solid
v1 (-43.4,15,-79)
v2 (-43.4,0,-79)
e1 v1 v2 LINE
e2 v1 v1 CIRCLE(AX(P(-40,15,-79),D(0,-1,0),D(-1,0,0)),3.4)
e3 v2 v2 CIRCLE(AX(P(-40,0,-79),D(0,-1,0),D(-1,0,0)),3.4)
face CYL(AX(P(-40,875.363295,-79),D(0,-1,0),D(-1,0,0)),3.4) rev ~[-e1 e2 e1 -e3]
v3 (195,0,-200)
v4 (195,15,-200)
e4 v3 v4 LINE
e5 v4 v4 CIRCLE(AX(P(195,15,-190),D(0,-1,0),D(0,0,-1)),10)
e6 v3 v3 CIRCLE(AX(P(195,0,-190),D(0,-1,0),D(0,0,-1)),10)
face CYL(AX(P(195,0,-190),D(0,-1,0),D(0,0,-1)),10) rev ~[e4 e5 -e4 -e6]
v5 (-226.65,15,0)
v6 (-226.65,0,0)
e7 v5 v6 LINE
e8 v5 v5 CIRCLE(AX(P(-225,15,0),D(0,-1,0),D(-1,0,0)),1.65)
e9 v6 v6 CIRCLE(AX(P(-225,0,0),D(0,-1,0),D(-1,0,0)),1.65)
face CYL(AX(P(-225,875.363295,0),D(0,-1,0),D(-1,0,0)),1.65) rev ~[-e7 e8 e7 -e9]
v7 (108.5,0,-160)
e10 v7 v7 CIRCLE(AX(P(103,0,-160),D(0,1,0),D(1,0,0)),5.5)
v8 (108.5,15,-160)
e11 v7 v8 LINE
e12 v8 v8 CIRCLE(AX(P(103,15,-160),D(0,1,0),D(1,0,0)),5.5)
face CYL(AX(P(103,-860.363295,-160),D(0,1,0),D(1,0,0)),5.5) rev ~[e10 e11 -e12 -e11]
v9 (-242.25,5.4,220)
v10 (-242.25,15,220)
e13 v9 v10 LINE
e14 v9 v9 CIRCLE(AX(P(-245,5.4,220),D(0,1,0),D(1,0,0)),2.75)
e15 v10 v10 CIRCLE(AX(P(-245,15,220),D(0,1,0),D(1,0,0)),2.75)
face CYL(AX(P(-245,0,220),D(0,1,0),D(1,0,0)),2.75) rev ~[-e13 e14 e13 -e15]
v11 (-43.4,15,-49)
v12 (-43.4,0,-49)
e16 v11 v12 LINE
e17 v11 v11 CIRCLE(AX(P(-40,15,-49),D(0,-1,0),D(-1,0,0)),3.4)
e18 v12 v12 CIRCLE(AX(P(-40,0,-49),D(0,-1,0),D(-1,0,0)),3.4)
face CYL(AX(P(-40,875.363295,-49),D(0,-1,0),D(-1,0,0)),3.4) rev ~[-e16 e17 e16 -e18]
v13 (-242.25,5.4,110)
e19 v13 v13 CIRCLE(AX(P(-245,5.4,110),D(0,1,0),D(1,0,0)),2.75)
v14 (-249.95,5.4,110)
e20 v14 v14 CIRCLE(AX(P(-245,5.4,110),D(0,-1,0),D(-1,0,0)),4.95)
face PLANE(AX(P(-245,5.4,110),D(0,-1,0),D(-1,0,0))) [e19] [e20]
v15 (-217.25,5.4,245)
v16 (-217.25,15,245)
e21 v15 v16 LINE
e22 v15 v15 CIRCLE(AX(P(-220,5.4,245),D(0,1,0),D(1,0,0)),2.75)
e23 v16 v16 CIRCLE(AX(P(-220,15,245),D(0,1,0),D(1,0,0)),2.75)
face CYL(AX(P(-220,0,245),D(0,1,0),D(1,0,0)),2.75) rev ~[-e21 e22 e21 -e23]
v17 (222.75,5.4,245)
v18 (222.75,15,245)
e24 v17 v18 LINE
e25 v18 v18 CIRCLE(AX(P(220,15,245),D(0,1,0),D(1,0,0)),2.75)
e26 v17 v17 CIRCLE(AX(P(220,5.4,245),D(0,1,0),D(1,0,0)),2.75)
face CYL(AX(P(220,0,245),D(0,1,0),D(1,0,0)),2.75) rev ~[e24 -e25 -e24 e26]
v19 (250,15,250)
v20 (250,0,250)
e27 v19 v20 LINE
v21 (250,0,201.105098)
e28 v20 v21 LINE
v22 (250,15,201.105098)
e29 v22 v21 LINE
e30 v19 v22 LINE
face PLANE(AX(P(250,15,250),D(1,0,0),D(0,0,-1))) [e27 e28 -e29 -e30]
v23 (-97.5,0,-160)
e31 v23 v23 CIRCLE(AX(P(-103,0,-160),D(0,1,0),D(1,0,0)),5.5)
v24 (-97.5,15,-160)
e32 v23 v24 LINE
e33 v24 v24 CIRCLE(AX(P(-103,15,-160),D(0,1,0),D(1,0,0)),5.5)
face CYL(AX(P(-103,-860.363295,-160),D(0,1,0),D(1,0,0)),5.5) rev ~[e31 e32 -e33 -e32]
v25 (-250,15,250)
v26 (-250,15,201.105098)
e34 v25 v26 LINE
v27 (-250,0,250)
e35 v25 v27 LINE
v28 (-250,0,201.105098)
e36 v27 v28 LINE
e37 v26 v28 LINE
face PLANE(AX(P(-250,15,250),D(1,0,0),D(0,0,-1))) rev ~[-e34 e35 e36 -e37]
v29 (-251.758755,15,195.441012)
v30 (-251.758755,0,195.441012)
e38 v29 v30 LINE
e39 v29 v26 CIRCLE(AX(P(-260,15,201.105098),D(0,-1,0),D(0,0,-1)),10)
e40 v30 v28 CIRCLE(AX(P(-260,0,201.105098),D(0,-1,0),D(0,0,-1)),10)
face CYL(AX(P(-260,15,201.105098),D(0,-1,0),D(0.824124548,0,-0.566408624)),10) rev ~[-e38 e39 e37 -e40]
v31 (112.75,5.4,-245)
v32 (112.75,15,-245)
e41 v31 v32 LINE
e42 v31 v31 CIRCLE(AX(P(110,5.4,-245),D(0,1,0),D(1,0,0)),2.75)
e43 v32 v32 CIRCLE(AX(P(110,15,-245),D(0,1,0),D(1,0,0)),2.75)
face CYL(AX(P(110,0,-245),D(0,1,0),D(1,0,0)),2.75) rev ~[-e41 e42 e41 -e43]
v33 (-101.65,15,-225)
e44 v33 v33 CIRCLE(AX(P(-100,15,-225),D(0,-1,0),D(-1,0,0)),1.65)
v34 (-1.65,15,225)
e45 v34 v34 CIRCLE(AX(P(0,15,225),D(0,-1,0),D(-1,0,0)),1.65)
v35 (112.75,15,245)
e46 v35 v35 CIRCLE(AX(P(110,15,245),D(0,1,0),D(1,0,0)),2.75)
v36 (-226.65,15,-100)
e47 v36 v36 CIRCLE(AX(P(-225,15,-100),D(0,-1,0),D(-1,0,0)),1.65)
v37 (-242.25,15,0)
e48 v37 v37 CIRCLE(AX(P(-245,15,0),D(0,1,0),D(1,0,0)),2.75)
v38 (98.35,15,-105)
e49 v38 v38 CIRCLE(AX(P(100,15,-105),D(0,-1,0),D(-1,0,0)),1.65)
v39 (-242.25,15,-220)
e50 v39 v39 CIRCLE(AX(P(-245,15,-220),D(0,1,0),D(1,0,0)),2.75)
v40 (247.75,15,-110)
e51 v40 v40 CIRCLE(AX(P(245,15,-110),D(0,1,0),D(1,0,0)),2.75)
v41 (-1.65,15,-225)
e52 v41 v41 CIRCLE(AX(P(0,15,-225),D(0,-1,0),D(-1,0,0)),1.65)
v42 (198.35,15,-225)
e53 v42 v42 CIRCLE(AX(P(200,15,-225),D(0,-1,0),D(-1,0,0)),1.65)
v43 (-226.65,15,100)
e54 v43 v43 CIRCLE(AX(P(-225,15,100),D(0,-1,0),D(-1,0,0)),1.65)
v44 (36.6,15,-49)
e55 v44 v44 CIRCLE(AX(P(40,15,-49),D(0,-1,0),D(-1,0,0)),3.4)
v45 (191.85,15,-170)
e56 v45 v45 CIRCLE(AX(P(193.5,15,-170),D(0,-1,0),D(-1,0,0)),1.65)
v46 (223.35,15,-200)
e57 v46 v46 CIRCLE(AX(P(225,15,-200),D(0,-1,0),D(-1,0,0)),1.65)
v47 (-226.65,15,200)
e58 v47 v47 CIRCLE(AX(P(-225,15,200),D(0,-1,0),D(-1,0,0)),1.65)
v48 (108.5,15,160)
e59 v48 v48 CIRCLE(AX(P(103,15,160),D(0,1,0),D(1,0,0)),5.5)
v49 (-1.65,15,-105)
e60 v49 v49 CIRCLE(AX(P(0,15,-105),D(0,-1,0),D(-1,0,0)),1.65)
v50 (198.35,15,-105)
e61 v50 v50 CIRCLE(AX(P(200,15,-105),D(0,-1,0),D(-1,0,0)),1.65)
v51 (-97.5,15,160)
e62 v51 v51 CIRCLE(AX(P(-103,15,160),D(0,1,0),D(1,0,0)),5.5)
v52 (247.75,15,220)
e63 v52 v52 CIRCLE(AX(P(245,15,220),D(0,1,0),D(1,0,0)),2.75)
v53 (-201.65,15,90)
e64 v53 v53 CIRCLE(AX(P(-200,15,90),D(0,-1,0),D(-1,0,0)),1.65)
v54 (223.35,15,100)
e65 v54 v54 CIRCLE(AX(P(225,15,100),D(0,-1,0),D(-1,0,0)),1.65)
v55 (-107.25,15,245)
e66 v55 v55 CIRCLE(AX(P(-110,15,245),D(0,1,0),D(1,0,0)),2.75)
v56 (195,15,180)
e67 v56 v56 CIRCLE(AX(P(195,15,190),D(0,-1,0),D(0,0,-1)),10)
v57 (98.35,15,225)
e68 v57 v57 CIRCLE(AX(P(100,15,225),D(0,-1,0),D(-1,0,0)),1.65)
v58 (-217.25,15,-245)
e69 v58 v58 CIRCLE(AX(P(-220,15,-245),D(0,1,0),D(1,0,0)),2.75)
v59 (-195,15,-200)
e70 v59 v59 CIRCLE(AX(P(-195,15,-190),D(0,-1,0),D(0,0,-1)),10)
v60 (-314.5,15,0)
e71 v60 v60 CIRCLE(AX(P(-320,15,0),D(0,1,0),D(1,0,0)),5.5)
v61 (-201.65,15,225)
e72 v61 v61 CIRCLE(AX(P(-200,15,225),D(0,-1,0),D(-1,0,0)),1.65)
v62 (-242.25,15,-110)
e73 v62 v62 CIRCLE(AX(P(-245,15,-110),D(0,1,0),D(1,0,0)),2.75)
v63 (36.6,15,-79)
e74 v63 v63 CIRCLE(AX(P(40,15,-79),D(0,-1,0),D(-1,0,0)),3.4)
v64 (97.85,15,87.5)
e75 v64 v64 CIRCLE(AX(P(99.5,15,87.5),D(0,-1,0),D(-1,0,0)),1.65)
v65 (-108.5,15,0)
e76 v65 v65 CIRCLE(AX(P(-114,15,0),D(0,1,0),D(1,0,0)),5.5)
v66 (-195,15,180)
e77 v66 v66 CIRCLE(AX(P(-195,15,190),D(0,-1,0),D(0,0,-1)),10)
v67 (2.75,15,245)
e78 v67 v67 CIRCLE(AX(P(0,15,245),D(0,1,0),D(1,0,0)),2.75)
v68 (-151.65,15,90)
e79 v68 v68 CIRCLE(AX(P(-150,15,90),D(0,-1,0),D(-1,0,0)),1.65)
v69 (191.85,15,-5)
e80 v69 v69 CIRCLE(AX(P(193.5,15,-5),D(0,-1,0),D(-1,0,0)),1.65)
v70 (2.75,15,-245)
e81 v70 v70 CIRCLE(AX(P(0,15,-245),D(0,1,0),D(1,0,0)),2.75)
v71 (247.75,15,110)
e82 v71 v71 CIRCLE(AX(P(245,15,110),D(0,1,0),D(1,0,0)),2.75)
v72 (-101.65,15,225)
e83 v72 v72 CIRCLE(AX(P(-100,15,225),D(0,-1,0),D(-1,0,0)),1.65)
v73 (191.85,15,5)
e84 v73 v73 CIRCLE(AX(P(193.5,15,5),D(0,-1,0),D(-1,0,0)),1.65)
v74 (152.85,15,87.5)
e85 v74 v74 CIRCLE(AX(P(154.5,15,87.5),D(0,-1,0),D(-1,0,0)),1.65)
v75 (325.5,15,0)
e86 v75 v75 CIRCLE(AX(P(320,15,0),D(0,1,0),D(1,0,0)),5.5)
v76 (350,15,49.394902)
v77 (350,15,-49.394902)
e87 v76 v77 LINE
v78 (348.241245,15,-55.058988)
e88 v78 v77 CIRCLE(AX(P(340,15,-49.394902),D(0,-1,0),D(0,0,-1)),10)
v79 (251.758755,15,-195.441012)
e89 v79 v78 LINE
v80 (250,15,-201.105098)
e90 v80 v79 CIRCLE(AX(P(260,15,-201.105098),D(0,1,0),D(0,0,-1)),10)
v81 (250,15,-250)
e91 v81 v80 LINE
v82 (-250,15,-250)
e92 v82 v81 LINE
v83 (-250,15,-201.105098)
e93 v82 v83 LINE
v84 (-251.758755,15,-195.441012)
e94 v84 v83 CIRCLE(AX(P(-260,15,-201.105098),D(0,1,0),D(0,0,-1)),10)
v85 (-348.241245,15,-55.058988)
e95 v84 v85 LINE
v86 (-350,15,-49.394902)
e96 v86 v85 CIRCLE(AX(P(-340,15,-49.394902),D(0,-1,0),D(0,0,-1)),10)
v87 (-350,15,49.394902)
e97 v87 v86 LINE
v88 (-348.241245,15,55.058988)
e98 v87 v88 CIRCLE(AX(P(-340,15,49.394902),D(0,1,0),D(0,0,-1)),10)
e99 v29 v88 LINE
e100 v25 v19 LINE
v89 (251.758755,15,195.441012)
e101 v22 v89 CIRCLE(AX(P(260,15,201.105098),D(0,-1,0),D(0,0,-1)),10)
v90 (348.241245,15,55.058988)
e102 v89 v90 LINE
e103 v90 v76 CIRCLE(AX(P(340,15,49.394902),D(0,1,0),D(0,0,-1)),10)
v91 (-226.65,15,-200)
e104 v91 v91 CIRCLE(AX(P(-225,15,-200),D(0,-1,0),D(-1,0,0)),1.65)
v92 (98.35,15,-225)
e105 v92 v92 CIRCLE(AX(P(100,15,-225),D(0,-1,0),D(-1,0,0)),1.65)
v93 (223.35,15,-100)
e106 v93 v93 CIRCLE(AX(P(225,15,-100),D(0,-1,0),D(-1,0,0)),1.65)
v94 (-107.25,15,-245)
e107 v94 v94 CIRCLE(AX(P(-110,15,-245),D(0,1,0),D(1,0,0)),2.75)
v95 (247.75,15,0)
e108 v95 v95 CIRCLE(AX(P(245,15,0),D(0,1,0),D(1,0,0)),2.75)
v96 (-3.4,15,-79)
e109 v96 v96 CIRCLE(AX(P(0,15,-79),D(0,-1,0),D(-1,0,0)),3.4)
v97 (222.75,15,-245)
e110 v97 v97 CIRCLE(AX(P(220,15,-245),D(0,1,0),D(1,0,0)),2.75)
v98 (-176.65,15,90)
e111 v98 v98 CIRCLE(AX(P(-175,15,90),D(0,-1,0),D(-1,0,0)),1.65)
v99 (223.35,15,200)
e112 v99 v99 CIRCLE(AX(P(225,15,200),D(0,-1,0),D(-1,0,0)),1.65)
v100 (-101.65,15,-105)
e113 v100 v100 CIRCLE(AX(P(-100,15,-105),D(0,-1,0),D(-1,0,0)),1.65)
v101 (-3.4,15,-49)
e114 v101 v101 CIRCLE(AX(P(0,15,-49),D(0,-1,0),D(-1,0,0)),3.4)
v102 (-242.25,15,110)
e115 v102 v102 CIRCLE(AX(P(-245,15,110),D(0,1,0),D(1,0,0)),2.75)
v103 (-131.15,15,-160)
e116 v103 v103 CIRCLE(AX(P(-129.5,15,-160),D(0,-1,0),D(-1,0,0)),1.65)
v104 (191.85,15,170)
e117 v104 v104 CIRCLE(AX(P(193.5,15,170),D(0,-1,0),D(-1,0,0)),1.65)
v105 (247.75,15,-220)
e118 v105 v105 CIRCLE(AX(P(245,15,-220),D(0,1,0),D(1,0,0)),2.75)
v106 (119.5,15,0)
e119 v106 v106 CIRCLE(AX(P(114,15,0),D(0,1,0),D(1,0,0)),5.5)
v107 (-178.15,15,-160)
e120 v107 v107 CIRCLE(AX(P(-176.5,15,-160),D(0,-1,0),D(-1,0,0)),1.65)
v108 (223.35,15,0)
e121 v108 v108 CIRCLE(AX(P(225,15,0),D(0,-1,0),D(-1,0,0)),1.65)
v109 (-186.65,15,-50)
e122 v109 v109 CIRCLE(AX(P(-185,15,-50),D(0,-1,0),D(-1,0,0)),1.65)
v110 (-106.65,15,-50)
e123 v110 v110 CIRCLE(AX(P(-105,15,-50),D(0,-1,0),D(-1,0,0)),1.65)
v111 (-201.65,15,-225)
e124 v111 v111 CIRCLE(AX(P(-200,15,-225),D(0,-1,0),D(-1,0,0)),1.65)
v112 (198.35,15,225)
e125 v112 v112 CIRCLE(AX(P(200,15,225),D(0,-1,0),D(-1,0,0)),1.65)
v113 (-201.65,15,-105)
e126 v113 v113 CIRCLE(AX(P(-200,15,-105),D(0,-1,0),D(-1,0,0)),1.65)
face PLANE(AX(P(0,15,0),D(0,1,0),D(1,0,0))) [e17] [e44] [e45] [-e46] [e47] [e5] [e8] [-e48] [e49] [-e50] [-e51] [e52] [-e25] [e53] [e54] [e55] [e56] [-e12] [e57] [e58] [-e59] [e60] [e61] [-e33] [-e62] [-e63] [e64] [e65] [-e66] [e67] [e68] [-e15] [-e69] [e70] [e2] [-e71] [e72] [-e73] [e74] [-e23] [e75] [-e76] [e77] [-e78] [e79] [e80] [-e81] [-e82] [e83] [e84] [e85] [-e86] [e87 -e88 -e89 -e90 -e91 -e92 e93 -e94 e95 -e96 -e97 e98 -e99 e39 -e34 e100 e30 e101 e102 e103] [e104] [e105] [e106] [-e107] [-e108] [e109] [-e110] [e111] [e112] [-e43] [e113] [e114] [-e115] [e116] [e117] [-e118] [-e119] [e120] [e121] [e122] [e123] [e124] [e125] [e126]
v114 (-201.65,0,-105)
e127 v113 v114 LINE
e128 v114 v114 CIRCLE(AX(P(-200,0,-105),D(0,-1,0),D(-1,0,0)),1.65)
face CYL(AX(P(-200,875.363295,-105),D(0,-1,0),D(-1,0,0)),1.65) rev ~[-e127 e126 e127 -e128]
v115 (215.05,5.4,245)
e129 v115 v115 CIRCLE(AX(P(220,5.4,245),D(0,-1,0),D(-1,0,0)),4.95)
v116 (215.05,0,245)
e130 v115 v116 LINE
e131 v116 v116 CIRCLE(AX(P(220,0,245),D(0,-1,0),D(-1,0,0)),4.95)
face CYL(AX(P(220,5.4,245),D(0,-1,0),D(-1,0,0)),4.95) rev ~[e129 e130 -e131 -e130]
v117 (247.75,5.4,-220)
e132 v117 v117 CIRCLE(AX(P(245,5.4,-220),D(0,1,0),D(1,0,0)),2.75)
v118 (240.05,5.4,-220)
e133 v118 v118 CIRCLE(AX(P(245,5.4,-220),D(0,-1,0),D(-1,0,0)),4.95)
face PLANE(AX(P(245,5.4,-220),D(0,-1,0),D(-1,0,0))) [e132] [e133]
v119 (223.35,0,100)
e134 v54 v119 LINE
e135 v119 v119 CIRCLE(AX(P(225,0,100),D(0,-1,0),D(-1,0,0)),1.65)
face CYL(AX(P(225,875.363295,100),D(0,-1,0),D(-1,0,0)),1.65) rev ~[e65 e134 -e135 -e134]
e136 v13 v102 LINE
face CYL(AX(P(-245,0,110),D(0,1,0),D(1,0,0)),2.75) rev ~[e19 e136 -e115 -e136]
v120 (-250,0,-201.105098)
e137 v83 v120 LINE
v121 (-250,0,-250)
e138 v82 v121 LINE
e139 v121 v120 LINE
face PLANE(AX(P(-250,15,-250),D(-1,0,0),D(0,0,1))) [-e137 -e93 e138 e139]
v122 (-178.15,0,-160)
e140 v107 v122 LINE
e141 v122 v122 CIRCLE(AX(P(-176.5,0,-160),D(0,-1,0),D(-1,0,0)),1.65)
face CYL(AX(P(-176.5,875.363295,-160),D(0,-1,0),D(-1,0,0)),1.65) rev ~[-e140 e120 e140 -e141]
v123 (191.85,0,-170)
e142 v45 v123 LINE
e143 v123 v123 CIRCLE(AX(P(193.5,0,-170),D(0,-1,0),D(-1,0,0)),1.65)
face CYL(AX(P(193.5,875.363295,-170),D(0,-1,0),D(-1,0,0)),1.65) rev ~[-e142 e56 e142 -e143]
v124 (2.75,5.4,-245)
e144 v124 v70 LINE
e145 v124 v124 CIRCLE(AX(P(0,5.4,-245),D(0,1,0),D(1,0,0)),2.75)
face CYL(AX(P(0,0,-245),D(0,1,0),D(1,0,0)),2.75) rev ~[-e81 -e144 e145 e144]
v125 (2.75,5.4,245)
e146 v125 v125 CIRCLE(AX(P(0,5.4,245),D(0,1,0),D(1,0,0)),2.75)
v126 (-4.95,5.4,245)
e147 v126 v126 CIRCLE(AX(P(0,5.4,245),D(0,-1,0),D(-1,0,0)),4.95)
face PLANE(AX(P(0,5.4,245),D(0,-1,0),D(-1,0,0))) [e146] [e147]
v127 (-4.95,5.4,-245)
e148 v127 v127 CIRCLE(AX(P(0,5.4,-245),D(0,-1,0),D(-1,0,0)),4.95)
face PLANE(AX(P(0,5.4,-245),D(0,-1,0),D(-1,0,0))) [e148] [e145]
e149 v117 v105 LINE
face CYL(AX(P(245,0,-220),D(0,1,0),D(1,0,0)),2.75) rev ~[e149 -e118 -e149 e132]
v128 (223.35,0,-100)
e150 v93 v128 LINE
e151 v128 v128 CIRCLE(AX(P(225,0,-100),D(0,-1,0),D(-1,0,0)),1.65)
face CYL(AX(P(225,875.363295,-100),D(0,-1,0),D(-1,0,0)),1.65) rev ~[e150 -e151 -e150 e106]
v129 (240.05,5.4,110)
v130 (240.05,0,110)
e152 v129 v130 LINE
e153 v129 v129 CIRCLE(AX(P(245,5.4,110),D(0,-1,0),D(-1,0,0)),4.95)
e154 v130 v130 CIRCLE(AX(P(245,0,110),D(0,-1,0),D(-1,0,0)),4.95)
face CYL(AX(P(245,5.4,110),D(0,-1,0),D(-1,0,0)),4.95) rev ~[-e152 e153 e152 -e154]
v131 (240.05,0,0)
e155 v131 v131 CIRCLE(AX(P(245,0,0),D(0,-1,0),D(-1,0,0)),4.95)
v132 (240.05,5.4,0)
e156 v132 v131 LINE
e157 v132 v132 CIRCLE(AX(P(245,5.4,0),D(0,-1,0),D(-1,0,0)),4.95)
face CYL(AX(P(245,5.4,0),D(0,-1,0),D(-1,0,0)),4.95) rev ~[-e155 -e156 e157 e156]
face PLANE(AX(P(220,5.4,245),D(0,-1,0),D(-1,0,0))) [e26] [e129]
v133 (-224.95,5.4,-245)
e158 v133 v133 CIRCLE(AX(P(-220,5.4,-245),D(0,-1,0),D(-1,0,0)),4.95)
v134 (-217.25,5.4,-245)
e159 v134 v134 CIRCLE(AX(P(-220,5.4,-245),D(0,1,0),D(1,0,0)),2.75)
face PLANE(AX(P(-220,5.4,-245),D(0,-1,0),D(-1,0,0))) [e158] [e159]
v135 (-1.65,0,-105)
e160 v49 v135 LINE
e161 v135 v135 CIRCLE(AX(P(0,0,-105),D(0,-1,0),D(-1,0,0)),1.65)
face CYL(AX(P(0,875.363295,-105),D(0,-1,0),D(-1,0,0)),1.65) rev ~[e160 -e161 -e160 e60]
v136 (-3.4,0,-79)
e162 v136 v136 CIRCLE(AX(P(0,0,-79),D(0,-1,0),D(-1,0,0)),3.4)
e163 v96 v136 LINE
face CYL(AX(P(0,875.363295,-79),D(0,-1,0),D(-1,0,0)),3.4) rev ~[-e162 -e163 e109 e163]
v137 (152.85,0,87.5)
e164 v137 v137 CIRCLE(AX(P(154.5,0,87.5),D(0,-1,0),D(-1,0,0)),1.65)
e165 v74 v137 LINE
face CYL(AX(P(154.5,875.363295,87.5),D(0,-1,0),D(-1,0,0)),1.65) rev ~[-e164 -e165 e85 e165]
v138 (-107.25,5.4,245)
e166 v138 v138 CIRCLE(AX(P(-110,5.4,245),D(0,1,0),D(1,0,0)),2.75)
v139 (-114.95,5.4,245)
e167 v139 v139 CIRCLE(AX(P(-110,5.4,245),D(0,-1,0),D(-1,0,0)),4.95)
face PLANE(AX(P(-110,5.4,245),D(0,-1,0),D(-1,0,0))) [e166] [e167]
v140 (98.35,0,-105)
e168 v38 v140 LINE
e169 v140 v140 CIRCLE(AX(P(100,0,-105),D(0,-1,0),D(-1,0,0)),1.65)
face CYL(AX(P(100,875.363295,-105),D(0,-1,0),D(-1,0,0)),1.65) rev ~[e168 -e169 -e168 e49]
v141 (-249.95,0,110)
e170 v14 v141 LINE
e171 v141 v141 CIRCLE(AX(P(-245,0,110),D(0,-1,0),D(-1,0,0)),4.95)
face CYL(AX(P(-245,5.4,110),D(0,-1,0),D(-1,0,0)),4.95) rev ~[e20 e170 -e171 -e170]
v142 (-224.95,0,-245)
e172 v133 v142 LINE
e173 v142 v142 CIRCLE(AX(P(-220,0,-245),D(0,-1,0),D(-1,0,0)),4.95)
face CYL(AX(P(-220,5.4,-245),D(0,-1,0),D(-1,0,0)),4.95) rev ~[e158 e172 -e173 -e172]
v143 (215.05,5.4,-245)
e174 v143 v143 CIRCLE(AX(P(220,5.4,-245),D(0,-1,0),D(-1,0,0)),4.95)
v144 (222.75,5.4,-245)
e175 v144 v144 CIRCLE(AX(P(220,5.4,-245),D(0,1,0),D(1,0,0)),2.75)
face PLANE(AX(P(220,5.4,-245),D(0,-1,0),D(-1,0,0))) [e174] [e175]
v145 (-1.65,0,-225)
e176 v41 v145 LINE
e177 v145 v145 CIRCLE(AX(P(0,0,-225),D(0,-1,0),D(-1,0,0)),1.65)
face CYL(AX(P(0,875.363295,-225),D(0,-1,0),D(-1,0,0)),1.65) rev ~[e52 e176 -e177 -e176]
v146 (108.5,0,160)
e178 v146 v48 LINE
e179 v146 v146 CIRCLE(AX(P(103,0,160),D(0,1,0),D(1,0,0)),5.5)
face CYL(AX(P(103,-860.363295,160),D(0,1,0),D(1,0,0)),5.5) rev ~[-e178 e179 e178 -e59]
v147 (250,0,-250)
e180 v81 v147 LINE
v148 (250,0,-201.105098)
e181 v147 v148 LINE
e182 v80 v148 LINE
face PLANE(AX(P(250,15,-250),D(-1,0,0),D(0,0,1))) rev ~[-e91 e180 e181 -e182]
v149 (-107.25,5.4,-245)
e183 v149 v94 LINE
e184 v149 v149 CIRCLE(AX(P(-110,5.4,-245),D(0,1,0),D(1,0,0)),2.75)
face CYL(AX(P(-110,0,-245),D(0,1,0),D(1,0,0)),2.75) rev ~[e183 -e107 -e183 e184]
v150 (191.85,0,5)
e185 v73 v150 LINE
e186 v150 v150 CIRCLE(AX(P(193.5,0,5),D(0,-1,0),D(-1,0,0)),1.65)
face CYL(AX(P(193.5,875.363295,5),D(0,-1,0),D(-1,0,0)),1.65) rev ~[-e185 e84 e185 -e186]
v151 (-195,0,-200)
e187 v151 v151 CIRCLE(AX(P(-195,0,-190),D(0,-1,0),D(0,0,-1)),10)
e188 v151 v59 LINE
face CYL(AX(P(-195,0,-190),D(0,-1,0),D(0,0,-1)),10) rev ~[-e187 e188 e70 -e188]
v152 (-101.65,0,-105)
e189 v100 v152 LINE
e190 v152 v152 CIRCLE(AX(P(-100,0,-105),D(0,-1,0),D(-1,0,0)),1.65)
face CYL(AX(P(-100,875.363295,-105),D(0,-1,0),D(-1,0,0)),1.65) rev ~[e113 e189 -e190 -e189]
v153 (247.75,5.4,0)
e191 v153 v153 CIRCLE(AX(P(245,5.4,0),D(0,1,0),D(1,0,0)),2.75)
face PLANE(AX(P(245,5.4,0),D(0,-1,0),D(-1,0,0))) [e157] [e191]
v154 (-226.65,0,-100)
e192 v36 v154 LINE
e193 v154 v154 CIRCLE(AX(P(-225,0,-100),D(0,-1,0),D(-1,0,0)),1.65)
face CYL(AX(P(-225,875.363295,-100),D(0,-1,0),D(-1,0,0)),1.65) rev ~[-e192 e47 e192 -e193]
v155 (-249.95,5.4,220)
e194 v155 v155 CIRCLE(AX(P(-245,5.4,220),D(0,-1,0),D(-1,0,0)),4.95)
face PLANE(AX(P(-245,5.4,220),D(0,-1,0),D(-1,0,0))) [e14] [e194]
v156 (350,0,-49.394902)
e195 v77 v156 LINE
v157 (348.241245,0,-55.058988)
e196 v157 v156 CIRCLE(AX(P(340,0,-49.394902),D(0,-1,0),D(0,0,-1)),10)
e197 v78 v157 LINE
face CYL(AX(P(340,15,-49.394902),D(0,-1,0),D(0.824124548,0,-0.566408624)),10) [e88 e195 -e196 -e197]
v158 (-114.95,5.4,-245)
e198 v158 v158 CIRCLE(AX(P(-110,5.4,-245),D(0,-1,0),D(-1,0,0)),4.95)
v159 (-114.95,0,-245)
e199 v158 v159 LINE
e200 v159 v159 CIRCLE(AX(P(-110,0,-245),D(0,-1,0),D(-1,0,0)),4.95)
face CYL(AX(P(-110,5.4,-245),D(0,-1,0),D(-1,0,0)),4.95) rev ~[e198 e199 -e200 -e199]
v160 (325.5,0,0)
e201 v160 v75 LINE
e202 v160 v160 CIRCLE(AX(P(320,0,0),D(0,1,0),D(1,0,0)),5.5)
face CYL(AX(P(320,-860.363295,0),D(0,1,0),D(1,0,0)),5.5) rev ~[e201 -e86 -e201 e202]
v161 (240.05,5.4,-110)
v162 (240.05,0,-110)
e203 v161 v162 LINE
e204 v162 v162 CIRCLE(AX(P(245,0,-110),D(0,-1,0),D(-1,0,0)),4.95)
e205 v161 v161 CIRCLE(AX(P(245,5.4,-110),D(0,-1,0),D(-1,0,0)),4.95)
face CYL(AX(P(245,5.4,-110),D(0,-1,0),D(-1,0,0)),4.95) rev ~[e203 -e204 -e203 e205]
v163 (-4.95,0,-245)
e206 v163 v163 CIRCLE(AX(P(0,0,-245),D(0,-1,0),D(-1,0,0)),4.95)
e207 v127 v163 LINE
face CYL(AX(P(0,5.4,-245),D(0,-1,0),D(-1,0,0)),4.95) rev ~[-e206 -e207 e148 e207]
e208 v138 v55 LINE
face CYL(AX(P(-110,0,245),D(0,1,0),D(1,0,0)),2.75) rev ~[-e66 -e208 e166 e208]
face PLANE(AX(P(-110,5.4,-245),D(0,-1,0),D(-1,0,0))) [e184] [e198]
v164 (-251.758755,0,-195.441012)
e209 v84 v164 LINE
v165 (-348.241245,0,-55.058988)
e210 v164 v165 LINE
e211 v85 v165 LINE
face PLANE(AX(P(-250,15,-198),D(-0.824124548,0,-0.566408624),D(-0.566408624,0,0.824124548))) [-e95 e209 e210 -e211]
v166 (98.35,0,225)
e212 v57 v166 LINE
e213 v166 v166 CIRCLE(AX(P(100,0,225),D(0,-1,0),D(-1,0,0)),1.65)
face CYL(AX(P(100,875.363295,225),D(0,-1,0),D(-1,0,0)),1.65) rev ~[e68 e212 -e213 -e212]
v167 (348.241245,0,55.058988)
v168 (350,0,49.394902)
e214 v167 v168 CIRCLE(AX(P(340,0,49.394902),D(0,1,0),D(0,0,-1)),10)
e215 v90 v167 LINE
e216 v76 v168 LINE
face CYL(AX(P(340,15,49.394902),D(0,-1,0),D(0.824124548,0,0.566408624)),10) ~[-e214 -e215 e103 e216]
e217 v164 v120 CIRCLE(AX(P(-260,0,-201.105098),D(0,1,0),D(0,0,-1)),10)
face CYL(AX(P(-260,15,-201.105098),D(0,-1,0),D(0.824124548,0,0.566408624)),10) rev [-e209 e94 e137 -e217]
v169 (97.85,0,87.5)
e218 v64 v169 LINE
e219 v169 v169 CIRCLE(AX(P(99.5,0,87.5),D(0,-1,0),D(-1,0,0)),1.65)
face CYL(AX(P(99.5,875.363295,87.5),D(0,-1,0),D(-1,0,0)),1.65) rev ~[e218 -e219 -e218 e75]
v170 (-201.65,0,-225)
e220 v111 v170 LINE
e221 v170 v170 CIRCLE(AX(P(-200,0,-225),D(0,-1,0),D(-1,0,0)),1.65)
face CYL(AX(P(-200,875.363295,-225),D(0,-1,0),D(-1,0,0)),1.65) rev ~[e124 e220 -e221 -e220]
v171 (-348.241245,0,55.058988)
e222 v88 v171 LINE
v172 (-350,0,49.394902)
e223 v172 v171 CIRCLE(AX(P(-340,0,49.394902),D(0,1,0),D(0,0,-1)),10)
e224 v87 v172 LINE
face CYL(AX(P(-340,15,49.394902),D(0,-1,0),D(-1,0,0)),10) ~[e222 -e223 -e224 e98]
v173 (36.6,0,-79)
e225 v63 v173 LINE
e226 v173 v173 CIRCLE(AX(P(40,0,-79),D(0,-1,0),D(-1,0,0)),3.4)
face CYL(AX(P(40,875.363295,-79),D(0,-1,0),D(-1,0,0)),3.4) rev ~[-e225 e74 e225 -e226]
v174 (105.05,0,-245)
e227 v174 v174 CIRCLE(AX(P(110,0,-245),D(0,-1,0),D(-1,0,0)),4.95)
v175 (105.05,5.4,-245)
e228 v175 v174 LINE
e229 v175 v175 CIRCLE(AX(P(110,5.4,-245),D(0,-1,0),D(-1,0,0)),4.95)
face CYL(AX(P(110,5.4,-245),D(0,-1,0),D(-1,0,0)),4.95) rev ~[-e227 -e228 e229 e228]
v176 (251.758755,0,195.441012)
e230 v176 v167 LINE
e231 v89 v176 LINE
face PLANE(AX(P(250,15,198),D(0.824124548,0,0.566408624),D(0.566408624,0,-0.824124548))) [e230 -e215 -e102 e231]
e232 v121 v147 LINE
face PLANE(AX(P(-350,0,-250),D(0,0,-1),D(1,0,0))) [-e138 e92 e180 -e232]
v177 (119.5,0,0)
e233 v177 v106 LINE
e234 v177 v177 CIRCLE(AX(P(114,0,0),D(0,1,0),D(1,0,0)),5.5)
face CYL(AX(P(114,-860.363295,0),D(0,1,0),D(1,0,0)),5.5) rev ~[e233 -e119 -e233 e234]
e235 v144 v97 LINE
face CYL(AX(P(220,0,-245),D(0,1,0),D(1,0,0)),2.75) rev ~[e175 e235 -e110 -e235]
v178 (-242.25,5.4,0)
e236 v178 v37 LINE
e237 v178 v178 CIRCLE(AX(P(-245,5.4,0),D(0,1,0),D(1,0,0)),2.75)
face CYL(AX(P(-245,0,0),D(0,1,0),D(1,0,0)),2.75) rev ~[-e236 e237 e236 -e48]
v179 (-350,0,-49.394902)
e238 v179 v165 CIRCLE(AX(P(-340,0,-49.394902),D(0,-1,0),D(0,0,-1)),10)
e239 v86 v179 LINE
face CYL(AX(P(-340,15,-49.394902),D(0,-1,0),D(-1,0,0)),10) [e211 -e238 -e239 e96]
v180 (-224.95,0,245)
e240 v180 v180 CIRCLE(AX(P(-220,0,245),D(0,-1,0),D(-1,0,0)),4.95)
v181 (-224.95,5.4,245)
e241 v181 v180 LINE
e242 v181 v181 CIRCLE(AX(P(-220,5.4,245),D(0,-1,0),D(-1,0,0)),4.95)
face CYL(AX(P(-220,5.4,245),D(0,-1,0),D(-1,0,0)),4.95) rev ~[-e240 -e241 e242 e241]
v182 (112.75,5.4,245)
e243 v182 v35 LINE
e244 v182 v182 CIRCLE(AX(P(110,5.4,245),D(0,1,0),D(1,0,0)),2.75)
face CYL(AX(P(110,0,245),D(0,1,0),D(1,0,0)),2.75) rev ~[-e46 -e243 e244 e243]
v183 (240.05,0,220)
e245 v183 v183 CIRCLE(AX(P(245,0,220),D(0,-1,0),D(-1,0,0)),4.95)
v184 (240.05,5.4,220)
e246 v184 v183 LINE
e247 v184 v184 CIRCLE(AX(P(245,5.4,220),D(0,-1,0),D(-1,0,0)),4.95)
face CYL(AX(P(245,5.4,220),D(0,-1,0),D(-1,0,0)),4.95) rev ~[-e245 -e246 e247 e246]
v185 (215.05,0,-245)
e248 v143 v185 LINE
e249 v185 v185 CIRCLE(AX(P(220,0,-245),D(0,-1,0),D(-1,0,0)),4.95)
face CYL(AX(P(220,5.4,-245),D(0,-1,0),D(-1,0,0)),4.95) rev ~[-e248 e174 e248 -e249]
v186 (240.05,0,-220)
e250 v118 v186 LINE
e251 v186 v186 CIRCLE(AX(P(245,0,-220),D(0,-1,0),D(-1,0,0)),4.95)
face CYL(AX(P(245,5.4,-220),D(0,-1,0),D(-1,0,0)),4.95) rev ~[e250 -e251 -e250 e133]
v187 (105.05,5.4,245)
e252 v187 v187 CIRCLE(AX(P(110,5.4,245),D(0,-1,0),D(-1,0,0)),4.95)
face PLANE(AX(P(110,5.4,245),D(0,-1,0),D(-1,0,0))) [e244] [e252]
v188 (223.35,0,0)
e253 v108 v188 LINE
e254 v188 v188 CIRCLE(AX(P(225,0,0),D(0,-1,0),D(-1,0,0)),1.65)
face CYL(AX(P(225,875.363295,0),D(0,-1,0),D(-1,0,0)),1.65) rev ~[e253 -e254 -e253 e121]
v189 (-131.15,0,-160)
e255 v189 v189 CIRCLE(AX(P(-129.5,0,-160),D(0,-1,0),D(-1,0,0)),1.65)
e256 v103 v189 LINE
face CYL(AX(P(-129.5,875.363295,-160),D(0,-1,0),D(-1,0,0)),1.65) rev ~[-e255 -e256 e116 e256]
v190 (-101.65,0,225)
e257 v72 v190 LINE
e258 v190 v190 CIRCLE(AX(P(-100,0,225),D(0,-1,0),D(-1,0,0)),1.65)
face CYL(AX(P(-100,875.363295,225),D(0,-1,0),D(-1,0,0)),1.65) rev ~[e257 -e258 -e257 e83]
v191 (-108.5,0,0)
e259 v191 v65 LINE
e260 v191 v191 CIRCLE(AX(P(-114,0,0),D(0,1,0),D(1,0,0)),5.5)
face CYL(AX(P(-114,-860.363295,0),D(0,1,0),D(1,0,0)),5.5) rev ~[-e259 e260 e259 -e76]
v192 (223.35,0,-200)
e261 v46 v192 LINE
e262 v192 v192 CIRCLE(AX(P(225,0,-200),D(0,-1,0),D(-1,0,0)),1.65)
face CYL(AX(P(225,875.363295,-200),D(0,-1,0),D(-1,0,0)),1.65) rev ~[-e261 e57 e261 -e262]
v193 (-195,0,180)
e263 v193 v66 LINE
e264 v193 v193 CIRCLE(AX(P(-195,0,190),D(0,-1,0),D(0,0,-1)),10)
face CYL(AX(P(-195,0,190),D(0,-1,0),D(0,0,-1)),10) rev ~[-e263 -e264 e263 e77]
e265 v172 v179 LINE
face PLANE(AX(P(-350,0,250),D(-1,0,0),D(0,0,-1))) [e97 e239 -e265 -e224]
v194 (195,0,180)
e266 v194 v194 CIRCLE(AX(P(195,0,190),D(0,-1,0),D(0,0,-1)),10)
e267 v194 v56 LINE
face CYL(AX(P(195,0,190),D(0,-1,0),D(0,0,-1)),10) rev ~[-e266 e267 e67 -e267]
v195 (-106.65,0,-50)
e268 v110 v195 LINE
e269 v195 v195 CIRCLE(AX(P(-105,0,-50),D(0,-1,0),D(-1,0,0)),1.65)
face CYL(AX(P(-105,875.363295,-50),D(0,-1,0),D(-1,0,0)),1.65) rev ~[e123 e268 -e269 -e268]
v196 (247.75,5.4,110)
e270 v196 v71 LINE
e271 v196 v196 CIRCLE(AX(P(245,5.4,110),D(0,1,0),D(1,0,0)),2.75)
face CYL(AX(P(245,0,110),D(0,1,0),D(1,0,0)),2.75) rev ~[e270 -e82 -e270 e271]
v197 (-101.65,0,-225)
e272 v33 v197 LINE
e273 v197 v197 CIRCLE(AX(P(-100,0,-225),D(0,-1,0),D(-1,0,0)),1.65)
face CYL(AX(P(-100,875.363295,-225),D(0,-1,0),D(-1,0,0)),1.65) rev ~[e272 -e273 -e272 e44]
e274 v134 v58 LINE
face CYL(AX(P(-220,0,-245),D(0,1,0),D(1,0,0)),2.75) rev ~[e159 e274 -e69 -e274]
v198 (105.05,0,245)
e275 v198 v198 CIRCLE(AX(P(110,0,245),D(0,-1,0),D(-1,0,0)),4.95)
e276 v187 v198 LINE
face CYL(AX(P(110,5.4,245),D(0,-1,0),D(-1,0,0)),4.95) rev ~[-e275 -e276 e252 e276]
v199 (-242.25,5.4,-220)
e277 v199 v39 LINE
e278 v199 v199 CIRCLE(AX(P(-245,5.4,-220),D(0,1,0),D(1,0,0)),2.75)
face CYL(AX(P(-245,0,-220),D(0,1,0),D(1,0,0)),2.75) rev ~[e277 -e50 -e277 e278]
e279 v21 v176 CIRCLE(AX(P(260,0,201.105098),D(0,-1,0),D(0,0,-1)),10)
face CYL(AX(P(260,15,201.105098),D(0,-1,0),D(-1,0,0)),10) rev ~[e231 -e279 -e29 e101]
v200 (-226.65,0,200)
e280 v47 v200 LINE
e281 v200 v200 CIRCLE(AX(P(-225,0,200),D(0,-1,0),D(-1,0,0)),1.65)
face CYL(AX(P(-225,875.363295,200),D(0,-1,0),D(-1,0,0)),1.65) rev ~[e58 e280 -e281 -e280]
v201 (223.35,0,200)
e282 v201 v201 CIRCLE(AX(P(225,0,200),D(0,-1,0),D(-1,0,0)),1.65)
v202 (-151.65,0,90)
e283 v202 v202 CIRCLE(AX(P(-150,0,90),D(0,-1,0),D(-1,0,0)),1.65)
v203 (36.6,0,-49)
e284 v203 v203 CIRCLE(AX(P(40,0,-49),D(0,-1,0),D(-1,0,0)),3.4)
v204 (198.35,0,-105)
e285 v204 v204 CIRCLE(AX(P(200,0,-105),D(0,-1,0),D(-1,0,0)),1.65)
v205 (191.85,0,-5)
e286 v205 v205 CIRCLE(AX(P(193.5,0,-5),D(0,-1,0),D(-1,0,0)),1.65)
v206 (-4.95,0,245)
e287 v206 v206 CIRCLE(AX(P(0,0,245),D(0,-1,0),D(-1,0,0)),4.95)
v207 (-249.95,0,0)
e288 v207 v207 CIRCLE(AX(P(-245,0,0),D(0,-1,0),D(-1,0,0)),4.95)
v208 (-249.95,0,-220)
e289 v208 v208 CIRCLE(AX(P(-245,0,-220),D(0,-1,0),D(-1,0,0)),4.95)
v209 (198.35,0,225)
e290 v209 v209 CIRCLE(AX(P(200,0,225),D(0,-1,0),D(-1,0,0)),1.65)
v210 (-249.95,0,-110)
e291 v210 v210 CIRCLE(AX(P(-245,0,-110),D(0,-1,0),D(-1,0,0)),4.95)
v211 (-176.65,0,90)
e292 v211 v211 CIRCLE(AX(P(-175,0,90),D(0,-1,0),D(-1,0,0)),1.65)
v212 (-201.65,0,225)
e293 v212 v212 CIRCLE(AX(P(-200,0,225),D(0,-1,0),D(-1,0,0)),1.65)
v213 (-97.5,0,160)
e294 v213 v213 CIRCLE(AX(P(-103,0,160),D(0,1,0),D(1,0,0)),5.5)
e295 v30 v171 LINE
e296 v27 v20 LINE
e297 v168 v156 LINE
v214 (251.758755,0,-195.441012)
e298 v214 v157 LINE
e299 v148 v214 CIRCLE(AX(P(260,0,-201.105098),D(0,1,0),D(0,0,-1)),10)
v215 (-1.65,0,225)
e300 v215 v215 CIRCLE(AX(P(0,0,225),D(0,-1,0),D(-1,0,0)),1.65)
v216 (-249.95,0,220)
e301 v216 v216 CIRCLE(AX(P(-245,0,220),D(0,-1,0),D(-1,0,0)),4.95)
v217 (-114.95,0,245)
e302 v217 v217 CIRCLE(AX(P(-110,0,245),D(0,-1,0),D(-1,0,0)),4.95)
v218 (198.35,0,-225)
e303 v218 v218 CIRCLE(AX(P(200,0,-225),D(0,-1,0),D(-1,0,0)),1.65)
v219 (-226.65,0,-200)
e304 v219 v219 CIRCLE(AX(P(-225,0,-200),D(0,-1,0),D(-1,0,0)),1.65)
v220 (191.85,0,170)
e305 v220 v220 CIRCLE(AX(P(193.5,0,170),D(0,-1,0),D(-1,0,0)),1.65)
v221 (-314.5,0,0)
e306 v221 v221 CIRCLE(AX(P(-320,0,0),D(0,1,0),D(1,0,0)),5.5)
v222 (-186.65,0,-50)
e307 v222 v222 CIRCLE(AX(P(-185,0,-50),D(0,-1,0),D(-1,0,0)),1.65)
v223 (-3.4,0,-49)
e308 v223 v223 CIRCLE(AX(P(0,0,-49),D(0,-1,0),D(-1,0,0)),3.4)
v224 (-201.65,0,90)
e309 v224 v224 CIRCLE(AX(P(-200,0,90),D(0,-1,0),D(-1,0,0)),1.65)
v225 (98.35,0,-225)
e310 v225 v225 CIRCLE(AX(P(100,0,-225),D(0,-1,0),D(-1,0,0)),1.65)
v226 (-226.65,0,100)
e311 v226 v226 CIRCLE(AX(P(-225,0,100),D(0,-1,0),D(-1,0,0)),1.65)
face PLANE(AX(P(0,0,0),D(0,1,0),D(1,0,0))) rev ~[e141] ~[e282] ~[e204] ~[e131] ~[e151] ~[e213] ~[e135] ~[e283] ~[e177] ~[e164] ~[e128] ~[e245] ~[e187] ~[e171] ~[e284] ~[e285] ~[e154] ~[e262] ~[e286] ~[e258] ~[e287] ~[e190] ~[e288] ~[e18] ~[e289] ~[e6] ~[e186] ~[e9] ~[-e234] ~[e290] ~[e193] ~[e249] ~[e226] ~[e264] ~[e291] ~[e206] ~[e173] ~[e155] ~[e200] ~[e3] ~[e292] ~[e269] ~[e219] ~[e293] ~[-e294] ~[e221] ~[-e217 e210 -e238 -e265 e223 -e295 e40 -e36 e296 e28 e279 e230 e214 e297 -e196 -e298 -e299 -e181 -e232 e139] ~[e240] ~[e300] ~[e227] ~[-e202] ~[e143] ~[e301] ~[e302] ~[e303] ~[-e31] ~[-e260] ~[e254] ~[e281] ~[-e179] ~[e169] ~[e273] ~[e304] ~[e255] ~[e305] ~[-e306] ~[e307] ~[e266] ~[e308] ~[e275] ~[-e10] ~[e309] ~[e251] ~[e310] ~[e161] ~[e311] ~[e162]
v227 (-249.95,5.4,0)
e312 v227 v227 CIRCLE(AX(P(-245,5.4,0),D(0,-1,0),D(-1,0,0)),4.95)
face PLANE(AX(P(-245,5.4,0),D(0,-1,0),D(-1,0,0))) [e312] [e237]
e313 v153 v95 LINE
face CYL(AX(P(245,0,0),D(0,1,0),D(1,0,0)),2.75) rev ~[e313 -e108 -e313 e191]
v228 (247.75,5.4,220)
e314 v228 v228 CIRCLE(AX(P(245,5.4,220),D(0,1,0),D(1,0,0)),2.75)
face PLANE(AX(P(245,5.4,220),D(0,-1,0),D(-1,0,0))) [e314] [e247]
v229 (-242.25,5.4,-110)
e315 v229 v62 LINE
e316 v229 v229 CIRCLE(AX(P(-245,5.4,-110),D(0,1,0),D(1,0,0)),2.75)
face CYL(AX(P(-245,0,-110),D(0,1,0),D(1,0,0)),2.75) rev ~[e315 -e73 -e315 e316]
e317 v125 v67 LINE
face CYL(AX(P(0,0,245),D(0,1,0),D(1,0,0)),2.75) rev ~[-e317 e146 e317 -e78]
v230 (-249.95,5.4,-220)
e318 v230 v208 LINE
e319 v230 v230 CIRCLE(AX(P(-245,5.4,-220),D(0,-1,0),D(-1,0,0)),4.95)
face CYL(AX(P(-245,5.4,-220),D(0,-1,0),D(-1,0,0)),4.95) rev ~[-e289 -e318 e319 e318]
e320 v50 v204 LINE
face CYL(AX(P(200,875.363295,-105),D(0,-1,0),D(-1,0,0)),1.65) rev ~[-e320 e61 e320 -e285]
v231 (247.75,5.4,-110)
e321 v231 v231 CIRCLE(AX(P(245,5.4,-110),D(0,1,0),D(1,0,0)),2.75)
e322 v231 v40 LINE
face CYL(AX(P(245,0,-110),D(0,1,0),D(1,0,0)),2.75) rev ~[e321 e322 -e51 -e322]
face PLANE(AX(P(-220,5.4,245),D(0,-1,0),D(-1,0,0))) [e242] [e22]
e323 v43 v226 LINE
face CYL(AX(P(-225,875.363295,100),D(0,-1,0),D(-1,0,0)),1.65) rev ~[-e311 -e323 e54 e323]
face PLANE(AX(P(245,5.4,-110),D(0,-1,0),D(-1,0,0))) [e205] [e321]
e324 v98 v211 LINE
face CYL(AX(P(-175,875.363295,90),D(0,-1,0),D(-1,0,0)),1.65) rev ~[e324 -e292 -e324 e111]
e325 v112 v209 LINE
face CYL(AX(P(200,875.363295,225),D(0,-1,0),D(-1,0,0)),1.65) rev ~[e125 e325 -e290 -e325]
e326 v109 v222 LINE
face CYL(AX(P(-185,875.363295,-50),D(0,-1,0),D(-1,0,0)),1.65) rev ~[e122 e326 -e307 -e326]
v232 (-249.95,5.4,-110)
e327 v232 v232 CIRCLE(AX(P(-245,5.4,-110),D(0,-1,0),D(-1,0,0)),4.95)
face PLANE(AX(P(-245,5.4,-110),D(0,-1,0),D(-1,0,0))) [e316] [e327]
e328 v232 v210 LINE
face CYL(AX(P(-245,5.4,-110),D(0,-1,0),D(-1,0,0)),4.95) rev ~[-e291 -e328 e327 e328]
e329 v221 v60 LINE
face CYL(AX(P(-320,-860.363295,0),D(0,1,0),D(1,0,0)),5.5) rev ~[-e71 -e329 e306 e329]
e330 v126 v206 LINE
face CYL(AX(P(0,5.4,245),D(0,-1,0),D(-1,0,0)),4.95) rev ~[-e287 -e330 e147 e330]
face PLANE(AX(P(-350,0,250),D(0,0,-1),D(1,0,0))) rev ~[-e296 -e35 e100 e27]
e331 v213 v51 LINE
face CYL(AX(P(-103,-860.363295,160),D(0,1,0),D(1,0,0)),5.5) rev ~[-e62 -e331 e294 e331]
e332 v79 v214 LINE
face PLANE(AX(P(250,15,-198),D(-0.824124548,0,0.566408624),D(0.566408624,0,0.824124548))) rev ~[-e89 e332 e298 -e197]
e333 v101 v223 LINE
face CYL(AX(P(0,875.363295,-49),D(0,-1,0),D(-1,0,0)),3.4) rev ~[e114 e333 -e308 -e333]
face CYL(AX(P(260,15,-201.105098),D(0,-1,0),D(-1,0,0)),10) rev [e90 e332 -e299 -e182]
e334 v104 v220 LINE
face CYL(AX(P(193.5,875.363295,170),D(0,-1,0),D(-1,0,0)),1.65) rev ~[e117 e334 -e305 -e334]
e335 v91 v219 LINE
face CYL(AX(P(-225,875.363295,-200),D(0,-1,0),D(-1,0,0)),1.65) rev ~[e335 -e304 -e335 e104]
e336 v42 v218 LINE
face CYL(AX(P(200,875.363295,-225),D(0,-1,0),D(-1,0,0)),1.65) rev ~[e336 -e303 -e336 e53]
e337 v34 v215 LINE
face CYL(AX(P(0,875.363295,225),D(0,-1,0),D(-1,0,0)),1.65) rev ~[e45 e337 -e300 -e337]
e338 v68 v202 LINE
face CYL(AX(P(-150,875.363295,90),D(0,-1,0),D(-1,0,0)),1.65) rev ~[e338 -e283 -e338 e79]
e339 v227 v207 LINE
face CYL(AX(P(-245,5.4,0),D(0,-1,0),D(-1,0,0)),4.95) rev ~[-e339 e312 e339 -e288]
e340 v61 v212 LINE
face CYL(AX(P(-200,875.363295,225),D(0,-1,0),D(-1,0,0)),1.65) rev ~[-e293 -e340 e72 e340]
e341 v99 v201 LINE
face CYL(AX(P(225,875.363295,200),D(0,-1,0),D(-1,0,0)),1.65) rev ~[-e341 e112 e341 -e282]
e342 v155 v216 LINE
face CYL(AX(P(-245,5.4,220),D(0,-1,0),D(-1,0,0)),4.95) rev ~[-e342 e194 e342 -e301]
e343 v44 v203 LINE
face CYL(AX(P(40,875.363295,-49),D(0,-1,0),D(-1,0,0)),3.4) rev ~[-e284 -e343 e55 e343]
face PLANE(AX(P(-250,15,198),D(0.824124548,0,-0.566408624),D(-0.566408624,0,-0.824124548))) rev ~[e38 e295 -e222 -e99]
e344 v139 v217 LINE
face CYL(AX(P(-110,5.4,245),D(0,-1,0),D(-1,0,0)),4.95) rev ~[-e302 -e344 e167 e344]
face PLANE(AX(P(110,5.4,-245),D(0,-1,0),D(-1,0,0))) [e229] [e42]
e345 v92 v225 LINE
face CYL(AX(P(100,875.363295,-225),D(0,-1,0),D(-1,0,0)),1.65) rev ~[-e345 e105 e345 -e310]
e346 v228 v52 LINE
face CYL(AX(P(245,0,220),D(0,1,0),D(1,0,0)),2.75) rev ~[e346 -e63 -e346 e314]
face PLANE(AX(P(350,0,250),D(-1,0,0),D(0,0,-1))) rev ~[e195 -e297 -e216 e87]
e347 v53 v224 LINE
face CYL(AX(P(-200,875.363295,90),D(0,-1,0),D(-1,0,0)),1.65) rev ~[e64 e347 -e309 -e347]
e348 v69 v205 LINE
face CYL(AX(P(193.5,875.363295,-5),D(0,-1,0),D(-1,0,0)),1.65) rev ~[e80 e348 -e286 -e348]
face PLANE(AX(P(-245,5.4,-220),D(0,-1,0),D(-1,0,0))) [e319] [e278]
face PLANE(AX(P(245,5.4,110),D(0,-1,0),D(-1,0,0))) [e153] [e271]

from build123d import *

# Parameters (mm, degrees)
SKETCH_1_W                   = 700
SKETCH_1_H                   = 500
EXTRUDE_1_DEPTH              = 15
CUT_EXTRUDE_1_DEPTH          = 431.37774106
HOLE_WIZARD_M5_2_D           = 5.5
HOLE_WIZARD_M5_2_CBORE_D     = 9.9
HOLE_WIZARD_M5_2_CBORE_DEPTH = 5.4
HOLE_WIZARD_M10_1_D          = 11
SKETCH_9_R                   = 10
CUT_EXTRUDE_2_DEPTH          = 431.37774106
HOLE_WIZARD_M8_2_D           = 6.8
HOLE_WIZARD_M4_1_D           = 3.3
HOLE_WIZARD_M4_2_D           = 3.3
FILLET_1_R                   = 10


with BuildPart() as part:
    # 草图1 → 凸台-拉伸1 (new body)
    with BuildSketch(Plane(origin=(0, 0, 0), x_dir=(1, 0, 0), z_dir=(0, 1, 0))):
        Rectangle(SKETCH_1_W, SKETCH_1_H)
    extrude(amount=EXTRUDE_1_DEPTH)

    # 草图2 → 切除-拉伸1 (cut, through all)
    with BuildSketch(Plane(origin=(0, 15, 0), x_dir=(1, 0, 0), z_dir=(0, 1, 0))):
        Polygon((-250, 250), (-250, 198), (-350, 52.5), (-350, 250), align=None)
        Polygon((350, 250), (250, 250), (250, 198), (350, 52.5), align=None)
        Polygon((250, -250), (250, -198), (350, -52.5), (350, -250), align=None)
        Polygon((-350, -250), (-250, -250), (-250, -198), (-350, -52.5), align=None)
    extrude(amount=-CUT_EXTRUDE_1_DEPTH, mode=Mode.SUBTRACT)

    # M5 六角凹头螺钉的柱形沉头孔2 (through all)
    with Locations(Plane(origin=(0, 0, 0), x_dir=(-1, 0, 0), z_dir=(0, -1, 0))):
        with Locations((-220, 245), (-110, 245), (0, 245), (110, 245), (220, 245), (245, 220), (245, 110), (245, 0), (245, -110), (245, -220), (220, -245), (110, -245), (0, -245), (-110, -245), (-220, -245), (-245, -220), (-245, -110), (-245, 0), (-245, 110), (-245, 220)):
            CounterBoreHole(HOLE_WIZARD_M5_2_D / 2, HOLE_WIZARD_M5_2_CBORE_D / 2, HOLE_WIZARD_M5_2_CBORE_DEPTH)

    # M10 间隙孔1 (through all)
    with Locations(Plane(origin=(0, 0, 0), x_dir=(-1, 0, 0), z_dir=(0, -1, 0))):
        with Locations((-320, 0), (-114, 0), (114, 0), (320, 0), (-103, 160), (103, 160), (103, -160), (-103, -160)):
            Hole(HOLE_WIZARD_M10_1_D / 2)

    # 草图9 → 切除-拉伸2 (cut, through all)
    with BuildSketch(Plane.XZ):
        with Locations(Location((195, 190, 0), (0, 0, 270))):
            Circle(SKETCH_9_R)
        with Locations(Location((195, -190, 0), (0, 0, 270))):
            Circle(SKETCH_9_R)
        with Locations(Location((-195, -190, 0), (0, 0, 270))):
            Circle(SKETCH_9_R)
        with Locations(Location((-195, 190, 0), (0, 0, 270))):
            Circle(SKETCH_9_R)
    extrude(amount=-CUT_EXTRUDE_2_DEPTH, mode=Mode.SUBTRACT)

    # M8 螺纹孔2 (through all)
    with Locations(Plane(origin=(0, 15, 0), x_dir=(1, 0, 0), z_dir=(0, 1, 0))):
        with Locations((-40, 79), (0, 79), (40, 79), (40, 49), (0, 49), (-40, 49)):
            Hole(HOLE_WIZARD_M8_2_D / 2)

    # M4 螺纹孔1 (through all)
    with Locations(Plane(origin=(0, 15, 0), x_dir=(1, 0, 0), z_dir=(0, 1, 0))):
        with Locations((0, 225), (100, 225), (200, 225), (-200, 225), (-100, 225), (225, 0), (225, 100), (225, 200), (225, -200), (225, -100), (-225, -100), (-225, -200), (-225, 200), (-225, 100), (-225, 0), (-100, -225), (-200, -225), (200, -225), (100, -225), (0, -225), (0, 105), (100, 105), (200, 105), (-200, 105), (-100, 105)):
            Hole(HOLE_WIZARD_M4_1_D / 2)

    # M4 螺纹孔2 (through all)
    with Locations(Plane(origin=(0, 15, 0), x_dir=(1, 0, 0), z_dir=(0, 1, 0))):
        with Locations((-185, 50), (-105, 50), (-176.5, 160), (-129.5, 160), (193.5, 170), (193.5, 5), (193.5, -5), (193.5, -170), (99.5, -87.5), (154.5, -87.5), (-150, -90), (-200, -90), (-175, -90)):
            Hole(HOLE_WIZARD_M4_2_D / 2)

    # 圆角1
    fillet_1_edges = [part.edges().sort_by_distance(p)[0] for p in [
        (-350, 7.5, 52.5),
        (-250, 7.5, 198),
        (250, 7.5, 198),
        (350, 7.5, 52.5),
        (350, 7.5, -52.5),
        (250, 7.5, -198),
        (-250, 7.5, -198),
        (-350, 7.5, -52.5),
    ]]
    fillet(fillet_1_edges, radius=FILLET_1_R)


solid = part.part
